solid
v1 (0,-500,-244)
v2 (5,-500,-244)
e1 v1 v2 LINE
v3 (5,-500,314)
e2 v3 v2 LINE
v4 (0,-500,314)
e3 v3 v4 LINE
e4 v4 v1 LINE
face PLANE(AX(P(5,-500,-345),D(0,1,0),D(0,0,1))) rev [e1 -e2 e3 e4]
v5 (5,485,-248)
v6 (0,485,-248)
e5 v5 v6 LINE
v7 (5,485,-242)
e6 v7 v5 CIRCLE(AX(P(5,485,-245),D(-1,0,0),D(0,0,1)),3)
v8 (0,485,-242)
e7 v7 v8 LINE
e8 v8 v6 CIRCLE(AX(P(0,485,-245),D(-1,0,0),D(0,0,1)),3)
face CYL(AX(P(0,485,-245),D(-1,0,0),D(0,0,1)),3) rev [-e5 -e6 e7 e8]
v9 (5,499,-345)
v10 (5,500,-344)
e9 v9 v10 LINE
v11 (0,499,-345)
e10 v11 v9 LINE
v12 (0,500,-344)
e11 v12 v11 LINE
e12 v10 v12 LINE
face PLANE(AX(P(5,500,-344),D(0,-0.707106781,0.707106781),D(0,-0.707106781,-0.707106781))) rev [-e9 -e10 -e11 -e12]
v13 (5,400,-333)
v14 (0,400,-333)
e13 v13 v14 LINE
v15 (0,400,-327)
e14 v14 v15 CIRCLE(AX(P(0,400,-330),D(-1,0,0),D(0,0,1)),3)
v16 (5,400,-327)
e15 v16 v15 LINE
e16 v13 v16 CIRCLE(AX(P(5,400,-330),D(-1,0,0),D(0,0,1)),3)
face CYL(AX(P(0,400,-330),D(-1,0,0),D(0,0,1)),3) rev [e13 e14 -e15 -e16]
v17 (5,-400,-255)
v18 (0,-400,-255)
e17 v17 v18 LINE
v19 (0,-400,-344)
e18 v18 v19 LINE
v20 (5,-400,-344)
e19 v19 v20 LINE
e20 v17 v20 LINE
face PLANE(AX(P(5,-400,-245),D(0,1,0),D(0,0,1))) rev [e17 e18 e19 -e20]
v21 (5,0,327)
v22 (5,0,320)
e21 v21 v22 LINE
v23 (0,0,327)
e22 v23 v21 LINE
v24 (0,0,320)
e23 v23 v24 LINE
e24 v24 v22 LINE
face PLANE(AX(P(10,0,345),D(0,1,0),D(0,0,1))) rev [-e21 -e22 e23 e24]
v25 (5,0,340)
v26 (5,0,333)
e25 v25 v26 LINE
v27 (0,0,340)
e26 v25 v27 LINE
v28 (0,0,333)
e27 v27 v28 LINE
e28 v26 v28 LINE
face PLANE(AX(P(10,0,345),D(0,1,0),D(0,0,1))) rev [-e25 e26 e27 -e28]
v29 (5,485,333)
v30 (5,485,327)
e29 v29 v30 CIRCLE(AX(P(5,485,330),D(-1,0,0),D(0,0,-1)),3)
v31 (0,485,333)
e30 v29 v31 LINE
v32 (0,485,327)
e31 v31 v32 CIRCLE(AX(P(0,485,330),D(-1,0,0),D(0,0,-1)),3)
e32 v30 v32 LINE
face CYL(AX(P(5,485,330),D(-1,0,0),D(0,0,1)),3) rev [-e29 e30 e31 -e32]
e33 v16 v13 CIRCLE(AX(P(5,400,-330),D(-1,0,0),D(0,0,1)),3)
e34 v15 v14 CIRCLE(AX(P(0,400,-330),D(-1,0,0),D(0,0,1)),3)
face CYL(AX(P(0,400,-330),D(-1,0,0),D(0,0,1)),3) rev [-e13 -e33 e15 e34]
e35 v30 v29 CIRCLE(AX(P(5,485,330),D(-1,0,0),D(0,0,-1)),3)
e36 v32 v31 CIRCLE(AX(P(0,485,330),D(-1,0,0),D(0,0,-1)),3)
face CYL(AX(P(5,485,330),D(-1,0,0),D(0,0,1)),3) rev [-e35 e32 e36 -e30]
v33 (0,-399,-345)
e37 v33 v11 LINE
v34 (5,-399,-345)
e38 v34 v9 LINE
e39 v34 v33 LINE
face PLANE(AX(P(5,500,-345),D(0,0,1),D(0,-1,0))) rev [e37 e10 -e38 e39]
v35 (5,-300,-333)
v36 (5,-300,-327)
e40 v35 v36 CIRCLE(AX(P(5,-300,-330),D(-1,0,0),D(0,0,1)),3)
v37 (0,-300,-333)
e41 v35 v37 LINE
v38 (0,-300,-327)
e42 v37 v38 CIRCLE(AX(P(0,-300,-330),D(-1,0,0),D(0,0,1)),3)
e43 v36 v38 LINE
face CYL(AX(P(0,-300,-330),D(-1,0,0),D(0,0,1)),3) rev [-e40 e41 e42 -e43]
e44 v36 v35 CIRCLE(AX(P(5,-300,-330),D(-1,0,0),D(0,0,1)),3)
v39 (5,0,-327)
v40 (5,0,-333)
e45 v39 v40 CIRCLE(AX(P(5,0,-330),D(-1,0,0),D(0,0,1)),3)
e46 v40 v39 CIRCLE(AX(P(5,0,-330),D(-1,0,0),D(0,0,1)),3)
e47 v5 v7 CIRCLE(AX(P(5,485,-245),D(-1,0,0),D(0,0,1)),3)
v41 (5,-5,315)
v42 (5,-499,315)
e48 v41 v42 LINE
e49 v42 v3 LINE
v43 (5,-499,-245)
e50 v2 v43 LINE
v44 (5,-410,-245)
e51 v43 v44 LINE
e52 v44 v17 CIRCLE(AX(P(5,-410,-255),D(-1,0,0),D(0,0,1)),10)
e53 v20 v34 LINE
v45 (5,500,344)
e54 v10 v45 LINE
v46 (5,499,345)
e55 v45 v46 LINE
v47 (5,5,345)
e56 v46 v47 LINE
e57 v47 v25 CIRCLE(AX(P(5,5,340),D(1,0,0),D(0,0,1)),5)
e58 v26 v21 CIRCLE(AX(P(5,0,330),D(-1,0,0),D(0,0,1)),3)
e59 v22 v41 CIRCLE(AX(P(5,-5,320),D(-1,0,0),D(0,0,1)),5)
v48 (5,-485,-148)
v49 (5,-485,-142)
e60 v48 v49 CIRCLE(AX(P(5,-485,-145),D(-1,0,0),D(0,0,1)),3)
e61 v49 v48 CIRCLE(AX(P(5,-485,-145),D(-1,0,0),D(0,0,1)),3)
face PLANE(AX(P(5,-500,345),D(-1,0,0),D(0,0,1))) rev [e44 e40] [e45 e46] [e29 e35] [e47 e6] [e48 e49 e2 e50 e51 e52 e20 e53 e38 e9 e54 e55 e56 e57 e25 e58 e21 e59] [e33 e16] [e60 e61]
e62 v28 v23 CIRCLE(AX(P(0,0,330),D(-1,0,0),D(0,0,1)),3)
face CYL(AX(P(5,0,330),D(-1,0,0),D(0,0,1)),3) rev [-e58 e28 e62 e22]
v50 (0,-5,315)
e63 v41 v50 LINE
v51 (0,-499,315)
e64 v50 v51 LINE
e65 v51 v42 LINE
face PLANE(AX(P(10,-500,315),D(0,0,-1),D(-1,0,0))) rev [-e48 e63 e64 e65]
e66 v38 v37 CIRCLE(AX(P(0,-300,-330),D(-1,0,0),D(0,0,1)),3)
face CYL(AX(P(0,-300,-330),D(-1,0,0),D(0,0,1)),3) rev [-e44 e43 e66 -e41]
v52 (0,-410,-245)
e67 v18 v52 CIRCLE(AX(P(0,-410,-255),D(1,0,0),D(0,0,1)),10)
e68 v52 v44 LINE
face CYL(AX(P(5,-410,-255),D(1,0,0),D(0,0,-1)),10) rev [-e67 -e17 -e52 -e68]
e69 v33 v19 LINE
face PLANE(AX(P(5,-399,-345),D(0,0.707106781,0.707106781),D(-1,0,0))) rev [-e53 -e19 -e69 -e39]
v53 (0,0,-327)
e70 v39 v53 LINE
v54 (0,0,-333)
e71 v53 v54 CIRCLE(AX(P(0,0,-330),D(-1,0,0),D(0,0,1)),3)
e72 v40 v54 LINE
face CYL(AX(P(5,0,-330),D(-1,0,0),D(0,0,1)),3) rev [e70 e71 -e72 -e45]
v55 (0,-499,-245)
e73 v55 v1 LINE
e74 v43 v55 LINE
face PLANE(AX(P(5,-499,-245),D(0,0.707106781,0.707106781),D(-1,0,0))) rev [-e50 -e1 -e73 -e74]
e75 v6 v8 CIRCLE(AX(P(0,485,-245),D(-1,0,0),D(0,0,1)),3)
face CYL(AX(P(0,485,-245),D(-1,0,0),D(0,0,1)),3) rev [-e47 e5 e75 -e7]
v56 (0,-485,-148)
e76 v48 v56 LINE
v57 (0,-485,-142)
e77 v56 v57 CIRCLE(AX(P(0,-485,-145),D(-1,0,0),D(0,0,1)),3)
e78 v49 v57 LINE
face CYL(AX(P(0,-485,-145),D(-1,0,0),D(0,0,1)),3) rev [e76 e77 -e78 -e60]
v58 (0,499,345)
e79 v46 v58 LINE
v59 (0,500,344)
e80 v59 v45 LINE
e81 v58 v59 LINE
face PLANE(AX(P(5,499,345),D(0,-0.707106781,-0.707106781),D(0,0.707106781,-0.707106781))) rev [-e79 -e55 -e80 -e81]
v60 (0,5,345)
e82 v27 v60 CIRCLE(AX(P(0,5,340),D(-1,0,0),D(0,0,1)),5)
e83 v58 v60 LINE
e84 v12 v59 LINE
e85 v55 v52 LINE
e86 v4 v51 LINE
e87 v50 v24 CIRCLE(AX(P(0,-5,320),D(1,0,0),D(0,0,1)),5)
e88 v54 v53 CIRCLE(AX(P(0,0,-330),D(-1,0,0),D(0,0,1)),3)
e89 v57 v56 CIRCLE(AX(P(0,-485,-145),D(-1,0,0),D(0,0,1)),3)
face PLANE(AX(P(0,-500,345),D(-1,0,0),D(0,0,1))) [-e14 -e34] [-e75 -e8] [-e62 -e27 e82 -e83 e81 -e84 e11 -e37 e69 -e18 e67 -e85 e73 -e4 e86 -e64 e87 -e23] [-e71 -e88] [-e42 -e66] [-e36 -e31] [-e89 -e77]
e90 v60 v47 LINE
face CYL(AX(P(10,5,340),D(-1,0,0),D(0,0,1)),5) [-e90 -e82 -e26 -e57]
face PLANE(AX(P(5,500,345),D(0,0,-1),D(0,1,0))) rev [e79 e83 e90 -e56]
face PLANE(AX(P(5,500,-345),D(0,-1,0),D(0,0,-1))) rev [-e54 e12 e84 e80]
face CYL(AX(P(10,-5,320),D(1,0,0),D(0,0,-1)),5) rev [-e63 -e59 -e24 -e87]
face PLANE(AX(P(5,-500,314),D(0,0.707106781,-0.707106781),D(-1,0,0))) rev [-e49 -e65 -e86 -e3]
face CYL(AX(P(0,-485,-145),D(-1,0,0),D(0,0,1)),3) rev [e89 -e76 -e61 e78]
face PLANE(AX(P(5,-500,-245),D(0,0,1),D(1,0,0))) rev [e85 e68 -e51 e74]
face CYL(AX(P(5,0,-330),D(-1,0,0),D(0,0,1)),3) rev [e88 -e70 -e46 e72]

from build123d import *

# Parameters (mm, degrees)
SKETCH_1_W                = 690
SKETCH_1_H                = 1000
EXTRUDE_1_DEPTH           = 5
CHAMFER_1_SIZE            = 1
SKETCH_2_R                = 3
CUT_EXTRUDE_1_DEPTH       = 608.494855945
SKETCH_3_W                = 100
SKETCH_3_H                = 100
CUT_EXTRUDE_2_DEPTH       = 608.494855945
HOLE_WIZARD_6_0_6_1_D     = 6
HOLE_WIZARD_6_0_6_1_DEPTH = 5
HOLE_WIZARD_6_0_6_1_TIP   = 3
FILLET_1_R                = 10
SKETCH_6_W                = 30
SKETCH_6_H                = 500
CUT_EXTRUDE_3_DEPTH       = 10
CHAMFER_2_SIZE            = 1
FILLET_2_R                = 5


with BuildPart() as part:
    # 草图1 → 凸台-拉伸1 (new body)
    with BuildSketch(Plane(origin=(0, 0, 0), x_dir=(0, 0, -1), z_dir=(1, 0, 0))):
        Rectangle(SKETCH_1_W, SKETCH_1_H)
    extrude(amount=EXTRUDE_1_DEPTH)

    # 倒角1
    chamfer_1_edges = [part.edges().sort_by_distance(p)[0] for p in [
        (2.5, 500, 345),
        (2.5, 500, -345),
        (2.5, -500, -345),
        (2.5, -500, 345),
    ]]
    chamfer(chamfer_1_edges, length=CHAMFER_1_SIZE)

    # 草图2 → 切除-拉伸1 (cut, through all)
    with BuildSketch(Plane.ZY):
        with Locations(Location((-330, -485, 0), (0, 0, 180))):
            Circle(SKETCH_2_R)
        with Locations((330, -485)):
            Circle(SKETCH_2_R)
        with Locations(Location((330, 485, 0), (0, 0, 180))):
            Circle(SKETCH_2_R)
        with Locations((330, 0)):
            Circle(SKETCH_2_R)
        with Locations((-330, 0)):
            Circle(SKETCH_2_R)
    extrude(amount=-CUT_EXTRUDE_1_DEPTH, mode=Mode.SUBTRACT)

    # 草图3 → 切除-拉伸2 (cut, through all)
    with BuildSketch(Plane.ZY):
        with Locations((-295, -450)):
            Rectangle(SKETCH_3_W, SKETCH_3_H)
    extrude(amount=-CUT_EXTRUDE_2_DEPTH, mode=Mode.SUBTRACT)

    # Ø6.0 (6) 直径孔1
    with Locations(Plane(origin=(0, -600, 465), x_dir=(0, 0, 1), z_dir=(-1, 0, 0))):
        with Locations((-710, 1085), (-795, 1000), (-795, 300), (-610, 115)):
            Hole(HOLE_WIZARD_6_0_6_1_D / 2, depth=HOLE_WIZARD_6_0_6_1_DEPTH)
            with Locations((0, 0, -(HOLE_WIZARD_6_0_6_1_DEPTH + HOLE_WIZARD_6_0_6_1_TIP / 2))):  # 90° drill point
                Cone(0, HOLE_WIZARD_6_0_6_1_D / 2, HOLE_WIZARD_6_0_6_1_TIP, mode=Mode.SUBTRACT)

    # 圆角1
    fillet_1_edges = [part.edges().sort_by_distance(p)[0] for p in [
        (2.5, -400, -245),
    ]]
    fillet(fillet_1_edges, radius=FILLET_1_R)

    # 草图6 → 切除-拉伸3 (cut)
    with BuildSketch(Plane.ZY):
        with Locations((330, -250)):
            Rectangle(SKETCH_6_W, SKETCH_6_H)
    extrude(amount=-CUT_EXTRUDE_3_DEPTH, mode=Mode.SUBTRACT)

    # 倒角2
    chamfer_2_edges = [part.edges().sort_by_distance(p)[0] for p in [
        (2.5, -500, 315),
        (2.5, -500, -245),
        (2.5, -400, -345),
    ]]
    chamfer(chamfer_2_edges, length=CHAMFER_2_SIZE)

    # 圆角2
    fillet_2_edges = [part.edges().sort_by_distance(p)[0] for p in [
        (2.5, 0, 345),
        (2.5, 0, 315),
    ]]
    fillet(fillet_2_edges, radius=FILLET_2_R)


solid = part.part
